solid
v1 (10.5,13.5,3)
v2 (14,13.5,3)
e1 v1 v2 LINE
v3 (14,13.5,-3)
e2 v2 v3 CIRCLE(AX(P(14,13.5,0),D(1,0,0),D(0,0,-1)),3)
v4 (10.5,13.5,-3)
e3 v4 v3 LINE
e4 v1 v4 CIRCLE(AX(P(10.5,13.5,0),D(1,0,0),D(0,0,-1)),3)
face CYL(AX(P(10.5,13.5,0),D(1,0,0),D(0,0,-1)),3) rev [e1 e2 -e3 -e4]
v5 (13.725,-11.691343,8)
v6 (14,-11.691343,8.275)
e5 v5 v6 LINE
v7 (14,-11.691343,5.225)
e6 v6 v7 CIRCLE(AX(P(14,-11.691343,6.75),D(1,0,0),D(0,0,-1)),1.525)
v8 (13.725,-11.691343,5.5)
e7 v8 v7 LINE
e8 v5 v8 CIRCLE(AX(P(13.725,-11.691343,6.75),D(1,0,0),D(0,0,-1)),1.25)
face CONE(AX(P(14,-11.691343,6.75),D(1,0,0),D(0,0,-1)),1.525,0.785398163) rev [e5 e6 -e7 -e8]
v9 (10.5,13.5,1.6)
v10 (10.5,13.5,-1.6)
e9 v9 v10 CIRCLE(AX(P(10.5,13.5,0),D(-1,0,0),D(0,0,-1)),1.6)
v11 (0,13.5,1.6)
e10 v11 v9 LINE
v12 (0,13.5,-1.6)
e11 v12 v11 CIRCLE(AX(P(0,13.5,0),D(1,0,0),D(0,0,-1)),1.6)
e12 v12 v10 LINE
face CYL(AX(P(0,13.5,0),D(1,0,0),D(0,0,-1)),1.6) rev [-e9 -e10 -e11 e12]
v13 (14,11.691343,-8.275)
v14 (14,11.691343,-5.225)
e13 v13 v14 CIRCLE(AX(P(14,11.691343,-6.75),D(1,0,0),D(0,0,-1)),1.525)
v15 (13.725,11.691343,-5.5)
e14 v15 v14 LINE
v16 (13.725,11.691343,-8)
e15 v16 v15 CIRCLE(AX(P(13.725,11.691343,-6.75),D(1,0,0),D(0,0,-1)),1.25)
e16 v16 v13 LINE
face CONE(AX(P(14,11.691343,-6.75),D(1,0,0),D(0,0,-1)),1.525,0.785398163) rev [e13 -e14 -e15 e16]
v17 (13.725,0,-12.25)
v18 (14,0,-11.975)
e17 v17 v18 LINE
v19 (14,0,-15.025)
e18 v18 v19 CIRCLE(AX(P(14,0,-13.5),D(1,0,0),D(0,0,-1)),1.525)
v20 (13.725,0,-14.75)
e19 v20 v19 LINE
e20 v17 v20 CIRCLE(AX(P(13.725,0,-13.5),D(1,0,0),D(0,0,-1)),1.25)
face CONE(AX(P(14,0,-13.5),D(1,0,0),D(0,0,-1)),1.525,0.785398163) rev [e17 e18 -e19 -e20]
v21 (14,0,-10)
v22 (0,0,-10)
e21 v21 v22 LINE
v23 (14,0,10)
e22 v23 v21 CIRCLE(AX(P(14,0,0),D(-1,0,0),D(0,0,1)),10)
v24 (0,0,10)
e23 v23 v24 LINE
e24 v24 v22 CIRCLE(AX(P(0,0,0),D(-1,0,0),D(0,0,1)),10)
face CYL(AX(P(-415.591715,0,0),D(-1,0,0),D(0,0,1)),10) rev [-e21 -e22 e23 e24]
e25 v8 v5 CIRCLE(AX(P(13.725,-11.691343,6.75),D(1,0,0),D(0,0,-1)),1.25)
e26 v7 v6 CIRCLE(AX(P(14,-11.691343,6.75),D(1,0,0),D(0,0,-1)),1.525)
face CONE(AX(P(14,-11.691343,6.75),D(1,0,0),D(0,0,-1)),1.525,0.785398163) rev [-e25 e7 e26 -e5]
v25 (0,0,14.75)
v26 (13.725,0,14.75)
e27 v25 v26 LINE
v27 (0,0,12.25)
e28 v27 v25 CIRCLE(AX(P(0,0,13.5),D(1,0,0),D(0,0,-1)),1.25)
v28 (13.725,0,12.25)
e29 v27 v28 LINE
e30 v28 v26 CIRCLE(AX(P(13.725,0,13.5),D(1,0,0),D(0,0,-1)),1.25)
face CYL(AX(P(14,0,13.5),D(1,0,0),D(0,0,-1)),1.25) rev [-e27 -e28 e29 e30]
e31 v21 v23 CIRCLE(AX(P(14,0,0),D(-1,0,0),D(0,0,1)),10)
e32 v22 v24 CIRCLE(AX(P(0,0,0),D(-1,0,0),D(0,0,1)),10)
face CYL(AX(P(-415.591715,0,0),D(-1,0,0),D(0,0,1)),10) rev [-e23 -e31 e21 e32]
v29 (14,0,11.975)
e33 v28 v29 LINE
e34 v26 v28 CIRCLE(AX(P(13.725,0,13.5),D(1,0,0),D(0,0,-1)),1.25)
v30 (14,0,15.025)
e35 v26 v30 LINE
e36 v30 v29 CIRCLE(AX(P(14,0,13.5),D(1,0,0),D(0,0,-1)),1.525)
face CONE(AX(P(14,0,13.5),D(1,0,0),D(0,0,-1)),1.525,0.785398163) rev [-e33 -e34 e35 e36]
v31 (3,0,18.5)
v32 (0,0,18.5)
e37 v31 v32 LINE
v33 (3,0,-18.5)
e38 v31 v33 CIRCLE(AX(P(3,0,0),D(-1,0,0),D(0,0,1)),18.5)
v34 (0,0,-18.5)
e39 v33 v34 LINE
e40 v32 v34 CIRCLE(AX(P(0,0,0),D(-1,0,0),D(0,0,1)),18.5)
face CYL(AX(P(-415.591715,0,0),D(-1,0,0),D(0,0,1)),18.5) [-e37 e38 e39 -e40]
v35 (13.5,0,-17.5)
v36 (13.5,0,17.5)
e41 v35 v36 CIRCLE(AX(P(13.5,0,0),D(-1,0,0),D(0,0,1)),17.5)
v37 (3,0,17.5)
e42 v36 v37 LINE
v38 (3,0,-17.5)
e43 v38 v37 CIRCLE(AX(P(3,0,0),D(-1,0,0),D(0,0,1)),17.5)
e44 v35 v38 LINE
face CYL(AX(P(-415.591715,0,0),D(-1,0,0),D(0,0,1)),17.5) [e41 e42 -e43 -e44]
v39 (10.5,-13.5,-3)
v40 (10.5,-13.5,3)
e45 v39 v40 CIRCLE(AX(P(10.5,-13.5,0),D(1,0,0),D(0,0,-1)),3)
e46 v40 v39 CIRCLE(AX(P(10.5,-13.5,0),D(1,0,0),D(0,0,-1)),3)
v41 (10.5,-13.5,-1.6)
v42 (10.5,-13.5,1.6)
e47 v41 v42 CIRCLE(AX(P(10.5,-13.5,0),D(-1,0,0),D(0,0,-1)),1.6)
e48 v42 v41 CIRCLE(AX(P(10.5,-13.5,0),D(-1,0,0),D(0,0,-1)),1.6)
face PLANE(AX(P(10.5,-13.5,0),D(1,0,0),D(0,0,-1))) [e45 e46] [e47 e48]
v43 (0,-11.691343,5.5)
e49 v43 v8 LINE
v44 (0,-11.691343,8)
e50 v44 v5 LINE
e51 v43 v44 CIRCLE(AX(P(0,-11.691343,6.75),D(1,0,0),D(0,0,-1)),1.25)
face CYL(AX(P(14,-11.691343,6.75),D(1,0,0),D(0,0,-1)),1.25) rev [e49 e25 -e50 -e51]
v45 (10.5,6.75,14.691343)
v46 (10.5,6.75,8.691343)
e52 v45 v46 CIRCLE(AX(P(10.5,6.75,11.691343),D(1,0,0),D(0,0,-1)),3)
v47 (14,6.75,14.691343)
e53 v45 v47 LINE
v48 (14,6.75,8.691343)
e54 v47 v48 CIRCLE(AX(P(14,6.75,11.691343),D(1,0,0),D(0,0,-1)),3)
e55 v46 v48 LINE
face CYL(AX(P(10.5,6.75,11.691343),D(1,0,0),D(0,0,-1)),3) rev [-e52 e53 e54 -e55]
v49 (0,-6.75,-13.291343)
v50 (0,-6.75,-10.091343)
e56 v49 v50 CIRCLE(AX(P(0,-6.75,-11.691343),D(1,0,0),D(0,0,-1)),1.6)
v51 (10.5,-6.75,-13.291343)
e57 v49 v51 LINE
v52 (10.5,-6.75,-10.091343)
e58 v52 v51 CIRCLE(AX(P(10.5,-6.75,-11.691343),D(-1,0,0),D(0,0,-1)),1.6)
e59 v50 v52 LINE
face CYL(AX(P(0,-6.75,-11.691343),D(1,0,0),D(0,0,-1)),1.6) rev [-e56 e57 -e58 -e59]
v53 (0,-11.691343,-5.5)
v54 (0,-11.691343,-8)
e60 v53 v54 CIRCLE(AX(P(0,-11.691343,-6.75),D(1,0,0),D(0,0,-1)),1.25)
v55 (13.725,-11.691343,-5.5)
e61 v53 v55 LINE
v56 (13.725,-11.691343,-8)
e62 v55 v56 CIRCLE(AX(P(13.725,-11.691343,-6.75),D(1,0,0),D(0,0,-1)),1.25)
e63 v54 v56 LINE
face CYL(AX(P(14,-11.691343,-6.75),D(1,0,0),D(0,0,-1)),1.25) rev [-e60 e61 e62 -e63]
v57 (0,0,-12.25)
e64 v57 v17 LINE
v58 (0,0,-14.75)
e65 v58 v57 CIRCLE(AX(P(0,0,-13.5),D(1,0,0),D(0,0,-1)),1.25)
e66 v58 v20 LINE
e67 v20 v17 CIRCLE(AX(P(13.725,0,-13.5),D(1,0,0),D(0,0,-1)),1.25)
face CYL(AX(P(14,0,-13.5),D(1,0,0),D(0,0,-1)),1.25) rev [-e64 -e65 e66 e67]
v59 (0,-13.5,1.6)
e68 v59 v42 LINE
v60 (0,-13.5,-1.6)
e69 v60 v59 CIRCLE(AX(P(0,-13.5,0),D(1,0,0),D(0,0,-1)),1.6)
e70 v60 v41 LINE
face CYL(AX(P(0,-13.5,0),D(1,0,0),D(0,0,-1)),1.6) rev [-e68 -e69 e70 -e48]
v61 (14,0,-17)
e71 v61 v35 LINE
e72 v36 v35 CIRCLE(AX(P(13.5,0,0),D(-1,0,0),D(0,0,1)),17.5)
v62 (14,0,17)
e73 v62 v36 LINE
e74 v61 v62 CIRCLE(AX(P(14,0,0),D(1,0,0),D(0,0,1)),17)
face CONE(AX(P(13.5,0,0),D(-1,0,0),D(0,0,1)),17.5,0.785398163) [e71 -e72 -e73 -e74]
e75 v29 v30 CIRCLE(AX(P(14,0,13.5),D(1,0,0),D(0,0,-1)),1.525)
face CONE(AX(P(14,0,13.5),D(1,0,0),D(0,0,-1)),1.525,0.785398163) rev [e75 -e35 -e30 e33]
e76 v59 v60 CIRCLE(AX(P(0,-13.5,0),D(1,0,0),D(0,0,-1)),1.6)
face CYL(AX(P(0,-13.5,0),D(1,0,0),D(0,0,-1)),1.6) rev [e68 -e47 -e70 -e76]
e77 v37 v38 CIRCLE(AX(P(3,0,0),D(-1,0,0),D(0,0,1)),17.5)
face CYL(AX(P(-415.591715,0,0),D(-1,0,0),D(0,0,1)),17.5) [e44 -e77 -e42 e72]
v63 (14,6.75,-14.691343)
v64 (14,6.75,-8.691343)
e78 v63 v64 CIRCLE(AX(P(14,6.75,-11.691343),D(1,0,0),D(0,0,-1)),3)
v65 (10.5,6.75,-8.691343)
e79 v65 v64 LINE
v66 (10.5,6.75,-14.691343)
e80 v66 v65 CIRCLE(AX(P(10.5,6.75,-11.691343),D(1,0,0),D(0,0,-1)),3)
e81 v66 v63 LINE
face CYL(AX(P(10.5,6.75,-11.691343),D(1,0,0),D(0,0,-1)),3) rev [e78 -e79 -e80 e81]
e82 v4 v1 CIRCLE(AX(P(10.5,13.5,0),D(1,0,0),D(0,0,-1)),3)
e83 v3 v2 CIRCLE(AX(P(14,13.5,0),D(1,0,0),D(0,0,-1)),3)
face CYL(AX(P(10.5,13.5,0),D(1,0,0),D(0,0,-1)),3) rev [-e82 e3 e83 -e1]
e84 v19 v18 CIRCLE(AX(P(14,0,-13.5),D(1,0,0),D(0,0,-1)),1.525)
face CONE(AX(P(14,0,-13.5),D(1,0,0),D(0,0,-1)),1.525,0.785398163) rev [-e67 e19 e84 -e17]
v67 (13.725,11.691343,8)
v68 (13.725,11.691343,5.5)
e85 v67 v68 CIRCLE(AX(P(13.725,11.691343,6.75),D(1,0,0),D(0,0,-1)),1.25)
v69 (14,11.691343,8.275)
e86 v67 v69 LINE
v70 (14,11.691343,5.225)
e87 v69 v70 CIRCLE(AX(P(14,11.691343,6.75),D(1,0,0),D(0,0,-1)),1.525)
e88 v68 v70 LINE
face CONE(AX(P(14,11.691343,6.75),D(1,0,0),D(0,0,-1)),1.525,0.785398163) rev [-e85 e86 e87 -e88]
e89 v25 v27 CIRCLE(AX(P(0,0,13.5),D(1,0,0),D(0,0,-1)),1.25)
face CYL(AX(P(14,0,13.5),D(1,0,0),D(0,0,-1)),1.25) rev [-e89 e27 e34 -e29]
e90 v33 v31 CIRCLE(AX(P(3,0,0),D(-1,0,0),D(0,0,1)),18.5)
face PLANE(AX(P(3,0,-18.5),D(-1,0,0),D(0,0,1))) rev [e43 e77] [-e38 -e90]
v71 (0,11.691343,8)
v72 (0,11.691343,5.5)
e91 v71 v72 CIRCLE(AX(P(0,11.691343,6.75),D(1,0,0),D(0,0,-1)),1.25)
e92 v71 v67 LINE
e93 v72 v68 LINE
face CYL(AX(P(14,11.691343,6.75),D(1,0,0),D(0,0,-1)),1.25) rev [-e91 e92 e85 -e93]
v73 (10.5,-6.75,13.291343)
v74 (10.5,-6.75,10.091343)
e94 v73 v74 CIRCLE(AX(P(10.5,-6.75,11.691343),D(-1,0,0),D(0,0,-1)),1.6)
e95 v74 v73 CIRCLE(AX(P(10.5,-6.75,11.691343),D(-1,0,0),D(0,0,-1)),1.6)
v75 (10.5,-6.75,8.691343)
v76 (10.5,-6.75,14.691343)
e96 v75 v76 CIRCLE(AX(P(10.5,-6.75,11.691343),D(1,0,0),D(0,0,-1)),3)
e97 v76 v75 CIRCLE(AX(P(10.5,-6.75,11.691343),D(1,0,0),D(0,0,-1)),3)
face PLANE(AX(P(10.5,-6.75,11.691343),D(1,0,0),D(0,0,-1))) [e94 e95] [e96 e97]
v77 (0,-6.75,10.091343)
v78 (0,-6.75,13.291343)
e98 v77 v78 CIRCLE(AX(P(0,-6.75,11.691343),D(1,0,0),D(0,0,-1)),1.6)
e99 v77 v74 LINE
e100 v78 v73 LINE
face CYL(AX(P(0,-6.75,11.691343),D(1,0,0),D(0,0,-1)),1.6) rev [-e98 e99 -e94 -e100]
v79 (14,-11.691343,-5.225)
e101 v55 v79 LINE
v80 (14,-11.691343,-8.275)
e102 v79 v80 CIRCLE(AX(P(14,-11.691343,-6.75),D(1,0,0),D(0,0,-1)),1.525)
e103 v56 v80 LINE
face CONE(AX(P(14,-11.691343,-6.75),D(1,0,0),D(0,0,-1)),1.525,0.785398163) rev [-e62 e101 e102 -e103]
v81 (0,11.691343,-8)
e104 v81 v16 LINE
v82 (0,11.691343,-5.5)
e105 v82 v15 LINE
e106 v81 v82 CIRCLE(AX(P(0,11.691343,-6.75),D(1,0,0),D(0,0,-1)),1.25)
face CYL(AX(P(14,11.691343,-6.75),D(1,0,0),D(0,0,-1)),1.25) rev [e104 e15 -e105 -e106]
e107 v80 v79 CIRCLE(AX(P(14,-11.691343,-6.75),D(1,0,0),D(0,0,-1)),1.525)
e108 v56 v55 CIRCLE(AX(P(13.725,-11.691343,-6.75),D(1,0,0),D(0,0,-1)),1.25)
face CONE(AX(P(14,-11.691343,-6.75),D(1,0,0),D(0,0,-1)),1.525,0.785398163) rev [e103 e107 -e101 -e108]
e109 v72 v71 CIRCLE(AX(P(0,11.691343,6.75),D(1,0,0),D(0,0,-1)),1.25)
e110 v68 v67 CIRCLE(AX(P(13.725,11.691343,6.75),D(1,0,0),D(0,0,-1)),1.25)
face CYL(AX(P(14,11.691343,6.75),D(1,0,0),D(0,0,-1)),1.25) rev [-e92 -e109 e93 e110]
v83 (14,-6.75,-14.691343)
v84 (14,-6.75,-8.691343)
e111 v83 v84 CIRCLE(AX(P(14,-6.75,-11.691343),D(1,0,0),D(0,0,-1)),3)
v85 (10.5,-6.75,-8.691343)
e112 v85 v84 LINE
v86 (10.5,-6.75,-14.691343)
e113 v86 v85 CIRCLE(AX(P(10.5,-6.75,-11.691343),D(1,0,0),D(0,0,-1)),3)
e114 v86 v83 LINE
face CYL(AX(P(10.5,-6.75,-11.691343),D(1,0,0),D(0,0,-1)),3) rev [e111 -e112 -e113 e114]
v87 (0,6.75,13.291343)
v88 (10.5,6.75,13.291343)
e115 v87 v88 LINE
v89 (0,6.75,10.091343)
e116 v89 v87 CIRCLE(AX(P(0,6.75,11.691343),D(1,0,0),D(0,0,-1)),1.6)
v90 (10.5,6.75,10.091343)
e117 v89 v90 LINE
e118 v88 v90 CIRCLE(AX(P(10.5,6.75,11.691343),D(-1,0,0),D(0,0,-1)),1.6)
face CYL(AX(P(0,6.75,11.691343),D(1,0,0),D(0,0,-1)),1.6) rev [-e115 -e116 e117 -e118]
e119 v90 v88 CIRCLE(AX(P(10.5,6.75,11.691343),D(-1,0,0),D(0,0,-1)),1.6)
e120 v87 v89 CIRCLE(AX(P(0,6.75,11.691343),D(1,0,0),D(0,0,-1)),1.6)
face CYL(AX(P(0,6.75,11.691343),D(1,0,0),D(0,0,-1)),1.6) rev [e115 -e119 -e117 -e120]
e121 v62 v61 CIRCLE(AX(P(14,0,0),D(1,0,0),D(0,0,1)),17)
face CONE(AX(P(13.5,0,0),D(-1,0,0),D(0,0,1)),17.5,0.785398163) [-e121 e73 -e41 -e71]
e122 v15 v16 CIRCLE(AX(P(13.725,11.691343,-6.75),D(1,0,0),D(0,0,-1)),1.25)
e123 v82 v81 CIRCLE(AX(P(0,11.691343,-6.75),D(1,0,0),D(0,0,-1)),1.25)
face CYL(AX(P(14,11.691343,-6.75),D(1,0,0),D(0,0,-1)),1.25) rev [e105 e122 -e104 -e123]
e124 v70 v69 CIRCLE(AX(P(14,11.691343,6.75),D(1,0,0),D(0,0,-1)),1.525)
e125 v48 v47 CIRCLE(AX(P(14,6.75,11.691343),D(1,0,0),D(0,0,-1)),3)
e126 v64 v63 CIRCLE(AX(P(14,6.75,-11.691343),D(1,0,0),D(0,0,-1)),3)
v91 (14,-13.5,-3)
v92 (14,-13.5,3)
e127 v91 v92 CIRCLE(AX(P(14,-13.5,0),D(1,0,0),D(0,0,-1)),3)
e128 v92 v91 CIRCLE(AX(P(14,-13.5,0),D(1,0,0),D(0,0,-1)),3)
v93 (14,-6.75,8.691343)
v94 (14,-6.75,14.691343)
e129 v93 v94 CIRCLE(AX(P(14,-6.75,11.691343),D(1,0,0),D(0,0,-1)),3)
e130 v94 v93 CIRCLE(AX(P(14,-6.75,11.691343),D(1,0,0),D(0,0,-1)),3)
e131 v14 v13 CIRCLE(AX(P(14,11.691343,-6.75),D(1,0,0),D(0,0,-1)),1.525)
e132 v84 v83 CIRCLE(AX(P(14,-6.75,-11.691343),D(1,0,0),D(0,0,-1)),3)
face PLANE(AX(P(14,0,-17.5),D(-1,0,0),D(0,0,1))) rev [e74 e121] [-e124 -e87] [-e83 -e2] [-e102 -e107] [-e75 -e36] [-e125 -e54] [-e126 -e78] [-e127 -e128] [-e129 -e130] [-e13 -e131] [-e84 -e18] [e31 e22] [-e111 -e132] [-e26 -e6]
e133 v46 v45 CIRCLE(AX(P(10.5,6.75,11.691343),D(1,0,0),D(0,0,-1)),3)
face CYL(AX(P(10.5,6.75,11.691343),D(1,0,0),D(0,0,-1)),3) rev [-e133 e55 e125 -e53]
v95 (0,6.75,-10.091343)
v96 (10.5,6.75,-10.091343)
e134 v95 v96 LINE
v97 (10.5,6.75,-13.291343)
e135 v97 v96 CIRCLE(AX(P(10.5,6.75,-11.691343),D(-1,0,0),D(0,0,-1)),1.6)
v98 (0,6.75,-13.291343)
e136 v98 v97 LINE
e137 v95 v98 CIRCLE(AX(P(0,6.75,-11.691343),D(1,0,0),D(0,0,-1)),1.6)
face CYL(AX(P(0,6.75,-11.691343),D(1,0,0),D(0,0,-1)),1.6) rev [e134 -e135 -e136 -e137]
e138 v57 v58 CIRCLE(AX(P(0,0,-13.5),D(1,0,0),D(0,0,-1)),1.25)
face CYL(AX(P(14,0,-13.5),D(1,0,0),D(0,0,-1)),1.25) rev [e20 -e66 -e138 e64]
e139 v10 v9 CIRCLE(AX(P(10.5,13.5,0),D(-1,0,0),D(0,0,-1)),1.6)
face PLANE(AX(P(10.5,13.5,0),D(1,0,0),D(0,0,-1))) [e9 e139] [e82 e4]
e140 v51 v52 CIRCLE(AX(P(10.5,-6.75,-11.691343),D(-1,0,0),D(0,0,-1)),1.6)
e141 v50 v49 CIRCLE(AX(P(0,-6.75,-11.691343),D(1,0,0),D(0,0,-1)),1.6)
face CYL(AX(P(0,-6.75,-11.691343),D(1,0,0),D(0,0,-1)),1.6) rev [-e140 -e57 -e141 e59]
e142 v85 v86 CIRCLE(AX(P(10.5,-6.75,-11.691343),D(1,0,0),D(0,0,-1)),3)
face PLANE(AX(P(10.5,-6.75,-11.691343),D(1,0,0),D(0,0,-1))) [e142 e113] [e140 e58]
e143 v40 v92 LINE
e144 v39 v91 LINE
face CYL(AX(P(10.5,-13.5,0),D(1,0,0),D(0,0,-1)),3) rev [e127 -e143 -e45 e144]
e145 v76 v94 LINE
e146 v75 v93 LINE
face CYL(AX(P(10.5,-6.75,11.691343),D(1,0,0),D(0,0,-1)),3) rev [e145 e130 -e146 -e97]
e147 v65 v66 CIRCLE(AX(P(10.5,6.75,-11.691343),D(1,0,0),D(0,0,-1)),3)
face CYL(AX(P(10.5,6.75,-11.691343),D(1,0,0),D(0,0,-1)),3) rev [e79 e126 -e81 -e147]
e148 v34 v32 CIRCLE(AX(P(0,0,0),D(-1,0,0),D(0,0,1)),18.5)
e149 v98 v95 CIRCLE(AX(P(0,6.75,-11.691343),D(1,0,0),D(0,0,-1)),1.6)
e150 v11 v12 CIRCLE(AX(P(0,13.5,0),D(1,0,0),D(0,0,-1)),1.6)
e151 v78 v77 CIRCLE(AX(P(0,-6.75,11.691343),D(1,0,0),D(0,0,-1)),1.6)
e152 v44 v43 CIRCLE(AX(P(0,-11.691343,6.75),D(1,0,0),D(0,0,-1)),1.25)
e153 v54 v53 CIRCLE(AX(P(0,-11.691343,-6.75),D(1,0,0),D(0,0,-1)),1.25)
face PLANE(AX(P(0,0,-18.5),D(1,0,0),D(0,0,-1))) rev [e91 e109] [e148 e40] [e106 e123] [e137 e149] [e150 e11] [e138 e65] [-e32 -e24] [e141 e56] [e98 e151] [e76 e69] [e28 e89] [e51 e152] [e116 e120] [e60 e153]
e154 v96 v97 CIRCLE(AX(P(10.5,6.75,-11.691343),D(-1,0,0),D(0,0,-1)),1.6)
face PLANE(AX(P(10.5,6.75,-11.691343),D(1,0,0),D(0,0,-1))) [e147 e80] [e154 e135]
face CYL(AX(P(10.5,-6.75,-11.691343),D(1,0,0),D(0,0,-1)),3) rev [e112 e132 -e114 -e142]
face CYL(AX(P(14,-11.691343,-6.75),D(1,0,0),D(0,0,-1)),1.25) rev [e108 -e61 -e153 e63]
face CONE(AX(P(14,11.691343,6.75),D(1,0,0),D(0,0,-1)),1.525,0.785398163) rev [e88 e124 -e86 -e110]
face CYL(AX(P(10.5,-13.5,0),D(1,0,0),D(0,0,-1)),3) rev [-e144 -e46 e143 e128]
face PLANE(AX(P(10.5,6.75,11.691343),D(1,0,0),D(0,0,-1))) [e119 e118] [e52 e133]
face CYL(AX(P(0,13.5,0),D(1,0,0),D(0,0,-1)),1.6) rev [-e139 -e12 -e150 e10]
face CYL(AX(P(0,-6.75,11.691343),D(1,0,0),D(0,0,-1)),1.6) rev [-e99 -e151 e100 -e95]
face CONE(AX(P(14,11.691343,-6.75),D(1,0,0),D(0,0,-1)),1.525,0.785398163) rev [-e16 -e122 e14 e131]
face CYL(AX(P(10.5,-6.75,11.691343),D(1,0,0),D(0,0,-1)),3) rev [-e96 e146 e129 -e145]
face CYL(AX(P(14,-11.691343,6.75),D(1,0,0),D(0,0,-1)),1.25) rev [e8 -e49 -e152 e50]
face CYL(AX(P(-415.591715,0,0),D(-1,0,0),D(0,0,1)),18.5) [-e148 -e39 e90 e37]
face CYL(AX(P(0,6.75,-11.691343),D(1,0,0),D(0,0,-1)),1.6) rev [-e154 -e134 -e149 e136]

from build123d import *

# Parameters (mm, degrees)
SKETCH_2_R                   = 1.6
CUT_EXTRUDE_1_DEPTH          = 30.67322025
CHAMFER_1_SIZE               = 0.5
SKETCH_3_R                   = 3
CUT_EXTRUDE_2_DEPTH          = 3.5
HOLE_WIZARD_M3_1_D           = 2.5
HOLE_WIZARD_M3_1_CSINK_D     = 3.05
HOLE_WIZARD_M3_1_CSINK_ANGLE = 90


with BuildPart() as part:
    # 草图1 → 旋转1 (revolve)
    with BuildSketch(Plane(origin=(0, 0, 0), x_dir=(1, 0, 0), z_dir=(0, 1, 0)), mode=Mode.PRIVATE) as revolve_1_sk:
        Polygon((0, 18.5), (3, 18.5), (3, 17.5), (14, 17.5), (14, 10), (0, 10), align=None)
    revolve(revolve_1_sk.sketch.rotate(Axis((-415.591715209, 0, 0), (1, 0, 0)), 180), axis=Axis((-415.591715209, 0, 0), (1, 0, 0)))

    # 草图2 → 切除-拉伸1 (cut, through all)
    with BuildSketch(Plane(origin=(14, 0, 0), x_dir=(0, 0, -1), z_dir=(1, 0, 0))):
        with Locations((0, 13.5)):
            Circle(SKETCH_2_R)
        with Locations((11.691342951, 6.75)):
            Circle(SKETCH_2_R)
        with Locations((11.691342951, -6.75)):
            Circle(SKETCH_2_R)
        with Locations((0, -13.5)):
            Circle(SKETCH_2_R)
        with Locations((-11.691342951, -6.75)):
            Circle(SKETCH_2_R)
        with Locations((-11.691342951, 6.75)):
            Circle(SKETCH_2_R)
    extrude(amount=-CUT_EXTRUDE_1_DEPTH, mode=Mode.SUBTRACT)

    # 倒角1
    chamfer_1_edges = [part.edges().sort_by_distance(p)[0] for p in [
        (14, 0, -17.5),
    ]]
    chamfer(chamfer_1_edges, length=CHAMFER_1_SIZE)

    # 草图3 → 切除-拉伸2 (cut)
    with BuildSketch(Plane(origin=(14, 0, 0), x_dir=(0, 0, -1), z_dir=(1, 0, 0))):
        with Locations((0, 13.5)):
            Circle(SKETCH_3_R)
        with Locations((11.691342951, 6.75)):
            Circle(SKETCH_3_R)
        with Locations((11.691342951, -6.75)):
            Circle(SKETCH_3_R)
        with Locations((0, -13.5)):
            Circle(SKETCH_3_R)
        with Locations((-11.691342951, -6.75)):
            Circle(SKETCH_3_R)
        with Locations((-11.691342951, 6.75)):
            Circle(SKETCH_3_R)
    extrude(amount=-CUT_EXTRUDE_2_DEPTH, mode=Mode.SUBTRACT)

    # M3 螺纹孔1 (through all)
    with Locations(Plane(origin=(14, 0, 0), x_dir=(0, 0, -1), z_dir=(1, 0, 0))):
        with Locations((-6.75, 11.691342951), (6.75, 11.691342951), (13.5, 0), (6.75, -11.691342951), (-6.75, -11.691342951), (-13.5, 0)):
            CounterSinkHole(HOLE_WIZARD_M3_1_D / 2, HOLE_WIZARD_M3_1_CSINK_D / 2, counter_sink_angle=HOLE_WIZARD_M3_1_CSINK_ANGLE)


solid = part.part
